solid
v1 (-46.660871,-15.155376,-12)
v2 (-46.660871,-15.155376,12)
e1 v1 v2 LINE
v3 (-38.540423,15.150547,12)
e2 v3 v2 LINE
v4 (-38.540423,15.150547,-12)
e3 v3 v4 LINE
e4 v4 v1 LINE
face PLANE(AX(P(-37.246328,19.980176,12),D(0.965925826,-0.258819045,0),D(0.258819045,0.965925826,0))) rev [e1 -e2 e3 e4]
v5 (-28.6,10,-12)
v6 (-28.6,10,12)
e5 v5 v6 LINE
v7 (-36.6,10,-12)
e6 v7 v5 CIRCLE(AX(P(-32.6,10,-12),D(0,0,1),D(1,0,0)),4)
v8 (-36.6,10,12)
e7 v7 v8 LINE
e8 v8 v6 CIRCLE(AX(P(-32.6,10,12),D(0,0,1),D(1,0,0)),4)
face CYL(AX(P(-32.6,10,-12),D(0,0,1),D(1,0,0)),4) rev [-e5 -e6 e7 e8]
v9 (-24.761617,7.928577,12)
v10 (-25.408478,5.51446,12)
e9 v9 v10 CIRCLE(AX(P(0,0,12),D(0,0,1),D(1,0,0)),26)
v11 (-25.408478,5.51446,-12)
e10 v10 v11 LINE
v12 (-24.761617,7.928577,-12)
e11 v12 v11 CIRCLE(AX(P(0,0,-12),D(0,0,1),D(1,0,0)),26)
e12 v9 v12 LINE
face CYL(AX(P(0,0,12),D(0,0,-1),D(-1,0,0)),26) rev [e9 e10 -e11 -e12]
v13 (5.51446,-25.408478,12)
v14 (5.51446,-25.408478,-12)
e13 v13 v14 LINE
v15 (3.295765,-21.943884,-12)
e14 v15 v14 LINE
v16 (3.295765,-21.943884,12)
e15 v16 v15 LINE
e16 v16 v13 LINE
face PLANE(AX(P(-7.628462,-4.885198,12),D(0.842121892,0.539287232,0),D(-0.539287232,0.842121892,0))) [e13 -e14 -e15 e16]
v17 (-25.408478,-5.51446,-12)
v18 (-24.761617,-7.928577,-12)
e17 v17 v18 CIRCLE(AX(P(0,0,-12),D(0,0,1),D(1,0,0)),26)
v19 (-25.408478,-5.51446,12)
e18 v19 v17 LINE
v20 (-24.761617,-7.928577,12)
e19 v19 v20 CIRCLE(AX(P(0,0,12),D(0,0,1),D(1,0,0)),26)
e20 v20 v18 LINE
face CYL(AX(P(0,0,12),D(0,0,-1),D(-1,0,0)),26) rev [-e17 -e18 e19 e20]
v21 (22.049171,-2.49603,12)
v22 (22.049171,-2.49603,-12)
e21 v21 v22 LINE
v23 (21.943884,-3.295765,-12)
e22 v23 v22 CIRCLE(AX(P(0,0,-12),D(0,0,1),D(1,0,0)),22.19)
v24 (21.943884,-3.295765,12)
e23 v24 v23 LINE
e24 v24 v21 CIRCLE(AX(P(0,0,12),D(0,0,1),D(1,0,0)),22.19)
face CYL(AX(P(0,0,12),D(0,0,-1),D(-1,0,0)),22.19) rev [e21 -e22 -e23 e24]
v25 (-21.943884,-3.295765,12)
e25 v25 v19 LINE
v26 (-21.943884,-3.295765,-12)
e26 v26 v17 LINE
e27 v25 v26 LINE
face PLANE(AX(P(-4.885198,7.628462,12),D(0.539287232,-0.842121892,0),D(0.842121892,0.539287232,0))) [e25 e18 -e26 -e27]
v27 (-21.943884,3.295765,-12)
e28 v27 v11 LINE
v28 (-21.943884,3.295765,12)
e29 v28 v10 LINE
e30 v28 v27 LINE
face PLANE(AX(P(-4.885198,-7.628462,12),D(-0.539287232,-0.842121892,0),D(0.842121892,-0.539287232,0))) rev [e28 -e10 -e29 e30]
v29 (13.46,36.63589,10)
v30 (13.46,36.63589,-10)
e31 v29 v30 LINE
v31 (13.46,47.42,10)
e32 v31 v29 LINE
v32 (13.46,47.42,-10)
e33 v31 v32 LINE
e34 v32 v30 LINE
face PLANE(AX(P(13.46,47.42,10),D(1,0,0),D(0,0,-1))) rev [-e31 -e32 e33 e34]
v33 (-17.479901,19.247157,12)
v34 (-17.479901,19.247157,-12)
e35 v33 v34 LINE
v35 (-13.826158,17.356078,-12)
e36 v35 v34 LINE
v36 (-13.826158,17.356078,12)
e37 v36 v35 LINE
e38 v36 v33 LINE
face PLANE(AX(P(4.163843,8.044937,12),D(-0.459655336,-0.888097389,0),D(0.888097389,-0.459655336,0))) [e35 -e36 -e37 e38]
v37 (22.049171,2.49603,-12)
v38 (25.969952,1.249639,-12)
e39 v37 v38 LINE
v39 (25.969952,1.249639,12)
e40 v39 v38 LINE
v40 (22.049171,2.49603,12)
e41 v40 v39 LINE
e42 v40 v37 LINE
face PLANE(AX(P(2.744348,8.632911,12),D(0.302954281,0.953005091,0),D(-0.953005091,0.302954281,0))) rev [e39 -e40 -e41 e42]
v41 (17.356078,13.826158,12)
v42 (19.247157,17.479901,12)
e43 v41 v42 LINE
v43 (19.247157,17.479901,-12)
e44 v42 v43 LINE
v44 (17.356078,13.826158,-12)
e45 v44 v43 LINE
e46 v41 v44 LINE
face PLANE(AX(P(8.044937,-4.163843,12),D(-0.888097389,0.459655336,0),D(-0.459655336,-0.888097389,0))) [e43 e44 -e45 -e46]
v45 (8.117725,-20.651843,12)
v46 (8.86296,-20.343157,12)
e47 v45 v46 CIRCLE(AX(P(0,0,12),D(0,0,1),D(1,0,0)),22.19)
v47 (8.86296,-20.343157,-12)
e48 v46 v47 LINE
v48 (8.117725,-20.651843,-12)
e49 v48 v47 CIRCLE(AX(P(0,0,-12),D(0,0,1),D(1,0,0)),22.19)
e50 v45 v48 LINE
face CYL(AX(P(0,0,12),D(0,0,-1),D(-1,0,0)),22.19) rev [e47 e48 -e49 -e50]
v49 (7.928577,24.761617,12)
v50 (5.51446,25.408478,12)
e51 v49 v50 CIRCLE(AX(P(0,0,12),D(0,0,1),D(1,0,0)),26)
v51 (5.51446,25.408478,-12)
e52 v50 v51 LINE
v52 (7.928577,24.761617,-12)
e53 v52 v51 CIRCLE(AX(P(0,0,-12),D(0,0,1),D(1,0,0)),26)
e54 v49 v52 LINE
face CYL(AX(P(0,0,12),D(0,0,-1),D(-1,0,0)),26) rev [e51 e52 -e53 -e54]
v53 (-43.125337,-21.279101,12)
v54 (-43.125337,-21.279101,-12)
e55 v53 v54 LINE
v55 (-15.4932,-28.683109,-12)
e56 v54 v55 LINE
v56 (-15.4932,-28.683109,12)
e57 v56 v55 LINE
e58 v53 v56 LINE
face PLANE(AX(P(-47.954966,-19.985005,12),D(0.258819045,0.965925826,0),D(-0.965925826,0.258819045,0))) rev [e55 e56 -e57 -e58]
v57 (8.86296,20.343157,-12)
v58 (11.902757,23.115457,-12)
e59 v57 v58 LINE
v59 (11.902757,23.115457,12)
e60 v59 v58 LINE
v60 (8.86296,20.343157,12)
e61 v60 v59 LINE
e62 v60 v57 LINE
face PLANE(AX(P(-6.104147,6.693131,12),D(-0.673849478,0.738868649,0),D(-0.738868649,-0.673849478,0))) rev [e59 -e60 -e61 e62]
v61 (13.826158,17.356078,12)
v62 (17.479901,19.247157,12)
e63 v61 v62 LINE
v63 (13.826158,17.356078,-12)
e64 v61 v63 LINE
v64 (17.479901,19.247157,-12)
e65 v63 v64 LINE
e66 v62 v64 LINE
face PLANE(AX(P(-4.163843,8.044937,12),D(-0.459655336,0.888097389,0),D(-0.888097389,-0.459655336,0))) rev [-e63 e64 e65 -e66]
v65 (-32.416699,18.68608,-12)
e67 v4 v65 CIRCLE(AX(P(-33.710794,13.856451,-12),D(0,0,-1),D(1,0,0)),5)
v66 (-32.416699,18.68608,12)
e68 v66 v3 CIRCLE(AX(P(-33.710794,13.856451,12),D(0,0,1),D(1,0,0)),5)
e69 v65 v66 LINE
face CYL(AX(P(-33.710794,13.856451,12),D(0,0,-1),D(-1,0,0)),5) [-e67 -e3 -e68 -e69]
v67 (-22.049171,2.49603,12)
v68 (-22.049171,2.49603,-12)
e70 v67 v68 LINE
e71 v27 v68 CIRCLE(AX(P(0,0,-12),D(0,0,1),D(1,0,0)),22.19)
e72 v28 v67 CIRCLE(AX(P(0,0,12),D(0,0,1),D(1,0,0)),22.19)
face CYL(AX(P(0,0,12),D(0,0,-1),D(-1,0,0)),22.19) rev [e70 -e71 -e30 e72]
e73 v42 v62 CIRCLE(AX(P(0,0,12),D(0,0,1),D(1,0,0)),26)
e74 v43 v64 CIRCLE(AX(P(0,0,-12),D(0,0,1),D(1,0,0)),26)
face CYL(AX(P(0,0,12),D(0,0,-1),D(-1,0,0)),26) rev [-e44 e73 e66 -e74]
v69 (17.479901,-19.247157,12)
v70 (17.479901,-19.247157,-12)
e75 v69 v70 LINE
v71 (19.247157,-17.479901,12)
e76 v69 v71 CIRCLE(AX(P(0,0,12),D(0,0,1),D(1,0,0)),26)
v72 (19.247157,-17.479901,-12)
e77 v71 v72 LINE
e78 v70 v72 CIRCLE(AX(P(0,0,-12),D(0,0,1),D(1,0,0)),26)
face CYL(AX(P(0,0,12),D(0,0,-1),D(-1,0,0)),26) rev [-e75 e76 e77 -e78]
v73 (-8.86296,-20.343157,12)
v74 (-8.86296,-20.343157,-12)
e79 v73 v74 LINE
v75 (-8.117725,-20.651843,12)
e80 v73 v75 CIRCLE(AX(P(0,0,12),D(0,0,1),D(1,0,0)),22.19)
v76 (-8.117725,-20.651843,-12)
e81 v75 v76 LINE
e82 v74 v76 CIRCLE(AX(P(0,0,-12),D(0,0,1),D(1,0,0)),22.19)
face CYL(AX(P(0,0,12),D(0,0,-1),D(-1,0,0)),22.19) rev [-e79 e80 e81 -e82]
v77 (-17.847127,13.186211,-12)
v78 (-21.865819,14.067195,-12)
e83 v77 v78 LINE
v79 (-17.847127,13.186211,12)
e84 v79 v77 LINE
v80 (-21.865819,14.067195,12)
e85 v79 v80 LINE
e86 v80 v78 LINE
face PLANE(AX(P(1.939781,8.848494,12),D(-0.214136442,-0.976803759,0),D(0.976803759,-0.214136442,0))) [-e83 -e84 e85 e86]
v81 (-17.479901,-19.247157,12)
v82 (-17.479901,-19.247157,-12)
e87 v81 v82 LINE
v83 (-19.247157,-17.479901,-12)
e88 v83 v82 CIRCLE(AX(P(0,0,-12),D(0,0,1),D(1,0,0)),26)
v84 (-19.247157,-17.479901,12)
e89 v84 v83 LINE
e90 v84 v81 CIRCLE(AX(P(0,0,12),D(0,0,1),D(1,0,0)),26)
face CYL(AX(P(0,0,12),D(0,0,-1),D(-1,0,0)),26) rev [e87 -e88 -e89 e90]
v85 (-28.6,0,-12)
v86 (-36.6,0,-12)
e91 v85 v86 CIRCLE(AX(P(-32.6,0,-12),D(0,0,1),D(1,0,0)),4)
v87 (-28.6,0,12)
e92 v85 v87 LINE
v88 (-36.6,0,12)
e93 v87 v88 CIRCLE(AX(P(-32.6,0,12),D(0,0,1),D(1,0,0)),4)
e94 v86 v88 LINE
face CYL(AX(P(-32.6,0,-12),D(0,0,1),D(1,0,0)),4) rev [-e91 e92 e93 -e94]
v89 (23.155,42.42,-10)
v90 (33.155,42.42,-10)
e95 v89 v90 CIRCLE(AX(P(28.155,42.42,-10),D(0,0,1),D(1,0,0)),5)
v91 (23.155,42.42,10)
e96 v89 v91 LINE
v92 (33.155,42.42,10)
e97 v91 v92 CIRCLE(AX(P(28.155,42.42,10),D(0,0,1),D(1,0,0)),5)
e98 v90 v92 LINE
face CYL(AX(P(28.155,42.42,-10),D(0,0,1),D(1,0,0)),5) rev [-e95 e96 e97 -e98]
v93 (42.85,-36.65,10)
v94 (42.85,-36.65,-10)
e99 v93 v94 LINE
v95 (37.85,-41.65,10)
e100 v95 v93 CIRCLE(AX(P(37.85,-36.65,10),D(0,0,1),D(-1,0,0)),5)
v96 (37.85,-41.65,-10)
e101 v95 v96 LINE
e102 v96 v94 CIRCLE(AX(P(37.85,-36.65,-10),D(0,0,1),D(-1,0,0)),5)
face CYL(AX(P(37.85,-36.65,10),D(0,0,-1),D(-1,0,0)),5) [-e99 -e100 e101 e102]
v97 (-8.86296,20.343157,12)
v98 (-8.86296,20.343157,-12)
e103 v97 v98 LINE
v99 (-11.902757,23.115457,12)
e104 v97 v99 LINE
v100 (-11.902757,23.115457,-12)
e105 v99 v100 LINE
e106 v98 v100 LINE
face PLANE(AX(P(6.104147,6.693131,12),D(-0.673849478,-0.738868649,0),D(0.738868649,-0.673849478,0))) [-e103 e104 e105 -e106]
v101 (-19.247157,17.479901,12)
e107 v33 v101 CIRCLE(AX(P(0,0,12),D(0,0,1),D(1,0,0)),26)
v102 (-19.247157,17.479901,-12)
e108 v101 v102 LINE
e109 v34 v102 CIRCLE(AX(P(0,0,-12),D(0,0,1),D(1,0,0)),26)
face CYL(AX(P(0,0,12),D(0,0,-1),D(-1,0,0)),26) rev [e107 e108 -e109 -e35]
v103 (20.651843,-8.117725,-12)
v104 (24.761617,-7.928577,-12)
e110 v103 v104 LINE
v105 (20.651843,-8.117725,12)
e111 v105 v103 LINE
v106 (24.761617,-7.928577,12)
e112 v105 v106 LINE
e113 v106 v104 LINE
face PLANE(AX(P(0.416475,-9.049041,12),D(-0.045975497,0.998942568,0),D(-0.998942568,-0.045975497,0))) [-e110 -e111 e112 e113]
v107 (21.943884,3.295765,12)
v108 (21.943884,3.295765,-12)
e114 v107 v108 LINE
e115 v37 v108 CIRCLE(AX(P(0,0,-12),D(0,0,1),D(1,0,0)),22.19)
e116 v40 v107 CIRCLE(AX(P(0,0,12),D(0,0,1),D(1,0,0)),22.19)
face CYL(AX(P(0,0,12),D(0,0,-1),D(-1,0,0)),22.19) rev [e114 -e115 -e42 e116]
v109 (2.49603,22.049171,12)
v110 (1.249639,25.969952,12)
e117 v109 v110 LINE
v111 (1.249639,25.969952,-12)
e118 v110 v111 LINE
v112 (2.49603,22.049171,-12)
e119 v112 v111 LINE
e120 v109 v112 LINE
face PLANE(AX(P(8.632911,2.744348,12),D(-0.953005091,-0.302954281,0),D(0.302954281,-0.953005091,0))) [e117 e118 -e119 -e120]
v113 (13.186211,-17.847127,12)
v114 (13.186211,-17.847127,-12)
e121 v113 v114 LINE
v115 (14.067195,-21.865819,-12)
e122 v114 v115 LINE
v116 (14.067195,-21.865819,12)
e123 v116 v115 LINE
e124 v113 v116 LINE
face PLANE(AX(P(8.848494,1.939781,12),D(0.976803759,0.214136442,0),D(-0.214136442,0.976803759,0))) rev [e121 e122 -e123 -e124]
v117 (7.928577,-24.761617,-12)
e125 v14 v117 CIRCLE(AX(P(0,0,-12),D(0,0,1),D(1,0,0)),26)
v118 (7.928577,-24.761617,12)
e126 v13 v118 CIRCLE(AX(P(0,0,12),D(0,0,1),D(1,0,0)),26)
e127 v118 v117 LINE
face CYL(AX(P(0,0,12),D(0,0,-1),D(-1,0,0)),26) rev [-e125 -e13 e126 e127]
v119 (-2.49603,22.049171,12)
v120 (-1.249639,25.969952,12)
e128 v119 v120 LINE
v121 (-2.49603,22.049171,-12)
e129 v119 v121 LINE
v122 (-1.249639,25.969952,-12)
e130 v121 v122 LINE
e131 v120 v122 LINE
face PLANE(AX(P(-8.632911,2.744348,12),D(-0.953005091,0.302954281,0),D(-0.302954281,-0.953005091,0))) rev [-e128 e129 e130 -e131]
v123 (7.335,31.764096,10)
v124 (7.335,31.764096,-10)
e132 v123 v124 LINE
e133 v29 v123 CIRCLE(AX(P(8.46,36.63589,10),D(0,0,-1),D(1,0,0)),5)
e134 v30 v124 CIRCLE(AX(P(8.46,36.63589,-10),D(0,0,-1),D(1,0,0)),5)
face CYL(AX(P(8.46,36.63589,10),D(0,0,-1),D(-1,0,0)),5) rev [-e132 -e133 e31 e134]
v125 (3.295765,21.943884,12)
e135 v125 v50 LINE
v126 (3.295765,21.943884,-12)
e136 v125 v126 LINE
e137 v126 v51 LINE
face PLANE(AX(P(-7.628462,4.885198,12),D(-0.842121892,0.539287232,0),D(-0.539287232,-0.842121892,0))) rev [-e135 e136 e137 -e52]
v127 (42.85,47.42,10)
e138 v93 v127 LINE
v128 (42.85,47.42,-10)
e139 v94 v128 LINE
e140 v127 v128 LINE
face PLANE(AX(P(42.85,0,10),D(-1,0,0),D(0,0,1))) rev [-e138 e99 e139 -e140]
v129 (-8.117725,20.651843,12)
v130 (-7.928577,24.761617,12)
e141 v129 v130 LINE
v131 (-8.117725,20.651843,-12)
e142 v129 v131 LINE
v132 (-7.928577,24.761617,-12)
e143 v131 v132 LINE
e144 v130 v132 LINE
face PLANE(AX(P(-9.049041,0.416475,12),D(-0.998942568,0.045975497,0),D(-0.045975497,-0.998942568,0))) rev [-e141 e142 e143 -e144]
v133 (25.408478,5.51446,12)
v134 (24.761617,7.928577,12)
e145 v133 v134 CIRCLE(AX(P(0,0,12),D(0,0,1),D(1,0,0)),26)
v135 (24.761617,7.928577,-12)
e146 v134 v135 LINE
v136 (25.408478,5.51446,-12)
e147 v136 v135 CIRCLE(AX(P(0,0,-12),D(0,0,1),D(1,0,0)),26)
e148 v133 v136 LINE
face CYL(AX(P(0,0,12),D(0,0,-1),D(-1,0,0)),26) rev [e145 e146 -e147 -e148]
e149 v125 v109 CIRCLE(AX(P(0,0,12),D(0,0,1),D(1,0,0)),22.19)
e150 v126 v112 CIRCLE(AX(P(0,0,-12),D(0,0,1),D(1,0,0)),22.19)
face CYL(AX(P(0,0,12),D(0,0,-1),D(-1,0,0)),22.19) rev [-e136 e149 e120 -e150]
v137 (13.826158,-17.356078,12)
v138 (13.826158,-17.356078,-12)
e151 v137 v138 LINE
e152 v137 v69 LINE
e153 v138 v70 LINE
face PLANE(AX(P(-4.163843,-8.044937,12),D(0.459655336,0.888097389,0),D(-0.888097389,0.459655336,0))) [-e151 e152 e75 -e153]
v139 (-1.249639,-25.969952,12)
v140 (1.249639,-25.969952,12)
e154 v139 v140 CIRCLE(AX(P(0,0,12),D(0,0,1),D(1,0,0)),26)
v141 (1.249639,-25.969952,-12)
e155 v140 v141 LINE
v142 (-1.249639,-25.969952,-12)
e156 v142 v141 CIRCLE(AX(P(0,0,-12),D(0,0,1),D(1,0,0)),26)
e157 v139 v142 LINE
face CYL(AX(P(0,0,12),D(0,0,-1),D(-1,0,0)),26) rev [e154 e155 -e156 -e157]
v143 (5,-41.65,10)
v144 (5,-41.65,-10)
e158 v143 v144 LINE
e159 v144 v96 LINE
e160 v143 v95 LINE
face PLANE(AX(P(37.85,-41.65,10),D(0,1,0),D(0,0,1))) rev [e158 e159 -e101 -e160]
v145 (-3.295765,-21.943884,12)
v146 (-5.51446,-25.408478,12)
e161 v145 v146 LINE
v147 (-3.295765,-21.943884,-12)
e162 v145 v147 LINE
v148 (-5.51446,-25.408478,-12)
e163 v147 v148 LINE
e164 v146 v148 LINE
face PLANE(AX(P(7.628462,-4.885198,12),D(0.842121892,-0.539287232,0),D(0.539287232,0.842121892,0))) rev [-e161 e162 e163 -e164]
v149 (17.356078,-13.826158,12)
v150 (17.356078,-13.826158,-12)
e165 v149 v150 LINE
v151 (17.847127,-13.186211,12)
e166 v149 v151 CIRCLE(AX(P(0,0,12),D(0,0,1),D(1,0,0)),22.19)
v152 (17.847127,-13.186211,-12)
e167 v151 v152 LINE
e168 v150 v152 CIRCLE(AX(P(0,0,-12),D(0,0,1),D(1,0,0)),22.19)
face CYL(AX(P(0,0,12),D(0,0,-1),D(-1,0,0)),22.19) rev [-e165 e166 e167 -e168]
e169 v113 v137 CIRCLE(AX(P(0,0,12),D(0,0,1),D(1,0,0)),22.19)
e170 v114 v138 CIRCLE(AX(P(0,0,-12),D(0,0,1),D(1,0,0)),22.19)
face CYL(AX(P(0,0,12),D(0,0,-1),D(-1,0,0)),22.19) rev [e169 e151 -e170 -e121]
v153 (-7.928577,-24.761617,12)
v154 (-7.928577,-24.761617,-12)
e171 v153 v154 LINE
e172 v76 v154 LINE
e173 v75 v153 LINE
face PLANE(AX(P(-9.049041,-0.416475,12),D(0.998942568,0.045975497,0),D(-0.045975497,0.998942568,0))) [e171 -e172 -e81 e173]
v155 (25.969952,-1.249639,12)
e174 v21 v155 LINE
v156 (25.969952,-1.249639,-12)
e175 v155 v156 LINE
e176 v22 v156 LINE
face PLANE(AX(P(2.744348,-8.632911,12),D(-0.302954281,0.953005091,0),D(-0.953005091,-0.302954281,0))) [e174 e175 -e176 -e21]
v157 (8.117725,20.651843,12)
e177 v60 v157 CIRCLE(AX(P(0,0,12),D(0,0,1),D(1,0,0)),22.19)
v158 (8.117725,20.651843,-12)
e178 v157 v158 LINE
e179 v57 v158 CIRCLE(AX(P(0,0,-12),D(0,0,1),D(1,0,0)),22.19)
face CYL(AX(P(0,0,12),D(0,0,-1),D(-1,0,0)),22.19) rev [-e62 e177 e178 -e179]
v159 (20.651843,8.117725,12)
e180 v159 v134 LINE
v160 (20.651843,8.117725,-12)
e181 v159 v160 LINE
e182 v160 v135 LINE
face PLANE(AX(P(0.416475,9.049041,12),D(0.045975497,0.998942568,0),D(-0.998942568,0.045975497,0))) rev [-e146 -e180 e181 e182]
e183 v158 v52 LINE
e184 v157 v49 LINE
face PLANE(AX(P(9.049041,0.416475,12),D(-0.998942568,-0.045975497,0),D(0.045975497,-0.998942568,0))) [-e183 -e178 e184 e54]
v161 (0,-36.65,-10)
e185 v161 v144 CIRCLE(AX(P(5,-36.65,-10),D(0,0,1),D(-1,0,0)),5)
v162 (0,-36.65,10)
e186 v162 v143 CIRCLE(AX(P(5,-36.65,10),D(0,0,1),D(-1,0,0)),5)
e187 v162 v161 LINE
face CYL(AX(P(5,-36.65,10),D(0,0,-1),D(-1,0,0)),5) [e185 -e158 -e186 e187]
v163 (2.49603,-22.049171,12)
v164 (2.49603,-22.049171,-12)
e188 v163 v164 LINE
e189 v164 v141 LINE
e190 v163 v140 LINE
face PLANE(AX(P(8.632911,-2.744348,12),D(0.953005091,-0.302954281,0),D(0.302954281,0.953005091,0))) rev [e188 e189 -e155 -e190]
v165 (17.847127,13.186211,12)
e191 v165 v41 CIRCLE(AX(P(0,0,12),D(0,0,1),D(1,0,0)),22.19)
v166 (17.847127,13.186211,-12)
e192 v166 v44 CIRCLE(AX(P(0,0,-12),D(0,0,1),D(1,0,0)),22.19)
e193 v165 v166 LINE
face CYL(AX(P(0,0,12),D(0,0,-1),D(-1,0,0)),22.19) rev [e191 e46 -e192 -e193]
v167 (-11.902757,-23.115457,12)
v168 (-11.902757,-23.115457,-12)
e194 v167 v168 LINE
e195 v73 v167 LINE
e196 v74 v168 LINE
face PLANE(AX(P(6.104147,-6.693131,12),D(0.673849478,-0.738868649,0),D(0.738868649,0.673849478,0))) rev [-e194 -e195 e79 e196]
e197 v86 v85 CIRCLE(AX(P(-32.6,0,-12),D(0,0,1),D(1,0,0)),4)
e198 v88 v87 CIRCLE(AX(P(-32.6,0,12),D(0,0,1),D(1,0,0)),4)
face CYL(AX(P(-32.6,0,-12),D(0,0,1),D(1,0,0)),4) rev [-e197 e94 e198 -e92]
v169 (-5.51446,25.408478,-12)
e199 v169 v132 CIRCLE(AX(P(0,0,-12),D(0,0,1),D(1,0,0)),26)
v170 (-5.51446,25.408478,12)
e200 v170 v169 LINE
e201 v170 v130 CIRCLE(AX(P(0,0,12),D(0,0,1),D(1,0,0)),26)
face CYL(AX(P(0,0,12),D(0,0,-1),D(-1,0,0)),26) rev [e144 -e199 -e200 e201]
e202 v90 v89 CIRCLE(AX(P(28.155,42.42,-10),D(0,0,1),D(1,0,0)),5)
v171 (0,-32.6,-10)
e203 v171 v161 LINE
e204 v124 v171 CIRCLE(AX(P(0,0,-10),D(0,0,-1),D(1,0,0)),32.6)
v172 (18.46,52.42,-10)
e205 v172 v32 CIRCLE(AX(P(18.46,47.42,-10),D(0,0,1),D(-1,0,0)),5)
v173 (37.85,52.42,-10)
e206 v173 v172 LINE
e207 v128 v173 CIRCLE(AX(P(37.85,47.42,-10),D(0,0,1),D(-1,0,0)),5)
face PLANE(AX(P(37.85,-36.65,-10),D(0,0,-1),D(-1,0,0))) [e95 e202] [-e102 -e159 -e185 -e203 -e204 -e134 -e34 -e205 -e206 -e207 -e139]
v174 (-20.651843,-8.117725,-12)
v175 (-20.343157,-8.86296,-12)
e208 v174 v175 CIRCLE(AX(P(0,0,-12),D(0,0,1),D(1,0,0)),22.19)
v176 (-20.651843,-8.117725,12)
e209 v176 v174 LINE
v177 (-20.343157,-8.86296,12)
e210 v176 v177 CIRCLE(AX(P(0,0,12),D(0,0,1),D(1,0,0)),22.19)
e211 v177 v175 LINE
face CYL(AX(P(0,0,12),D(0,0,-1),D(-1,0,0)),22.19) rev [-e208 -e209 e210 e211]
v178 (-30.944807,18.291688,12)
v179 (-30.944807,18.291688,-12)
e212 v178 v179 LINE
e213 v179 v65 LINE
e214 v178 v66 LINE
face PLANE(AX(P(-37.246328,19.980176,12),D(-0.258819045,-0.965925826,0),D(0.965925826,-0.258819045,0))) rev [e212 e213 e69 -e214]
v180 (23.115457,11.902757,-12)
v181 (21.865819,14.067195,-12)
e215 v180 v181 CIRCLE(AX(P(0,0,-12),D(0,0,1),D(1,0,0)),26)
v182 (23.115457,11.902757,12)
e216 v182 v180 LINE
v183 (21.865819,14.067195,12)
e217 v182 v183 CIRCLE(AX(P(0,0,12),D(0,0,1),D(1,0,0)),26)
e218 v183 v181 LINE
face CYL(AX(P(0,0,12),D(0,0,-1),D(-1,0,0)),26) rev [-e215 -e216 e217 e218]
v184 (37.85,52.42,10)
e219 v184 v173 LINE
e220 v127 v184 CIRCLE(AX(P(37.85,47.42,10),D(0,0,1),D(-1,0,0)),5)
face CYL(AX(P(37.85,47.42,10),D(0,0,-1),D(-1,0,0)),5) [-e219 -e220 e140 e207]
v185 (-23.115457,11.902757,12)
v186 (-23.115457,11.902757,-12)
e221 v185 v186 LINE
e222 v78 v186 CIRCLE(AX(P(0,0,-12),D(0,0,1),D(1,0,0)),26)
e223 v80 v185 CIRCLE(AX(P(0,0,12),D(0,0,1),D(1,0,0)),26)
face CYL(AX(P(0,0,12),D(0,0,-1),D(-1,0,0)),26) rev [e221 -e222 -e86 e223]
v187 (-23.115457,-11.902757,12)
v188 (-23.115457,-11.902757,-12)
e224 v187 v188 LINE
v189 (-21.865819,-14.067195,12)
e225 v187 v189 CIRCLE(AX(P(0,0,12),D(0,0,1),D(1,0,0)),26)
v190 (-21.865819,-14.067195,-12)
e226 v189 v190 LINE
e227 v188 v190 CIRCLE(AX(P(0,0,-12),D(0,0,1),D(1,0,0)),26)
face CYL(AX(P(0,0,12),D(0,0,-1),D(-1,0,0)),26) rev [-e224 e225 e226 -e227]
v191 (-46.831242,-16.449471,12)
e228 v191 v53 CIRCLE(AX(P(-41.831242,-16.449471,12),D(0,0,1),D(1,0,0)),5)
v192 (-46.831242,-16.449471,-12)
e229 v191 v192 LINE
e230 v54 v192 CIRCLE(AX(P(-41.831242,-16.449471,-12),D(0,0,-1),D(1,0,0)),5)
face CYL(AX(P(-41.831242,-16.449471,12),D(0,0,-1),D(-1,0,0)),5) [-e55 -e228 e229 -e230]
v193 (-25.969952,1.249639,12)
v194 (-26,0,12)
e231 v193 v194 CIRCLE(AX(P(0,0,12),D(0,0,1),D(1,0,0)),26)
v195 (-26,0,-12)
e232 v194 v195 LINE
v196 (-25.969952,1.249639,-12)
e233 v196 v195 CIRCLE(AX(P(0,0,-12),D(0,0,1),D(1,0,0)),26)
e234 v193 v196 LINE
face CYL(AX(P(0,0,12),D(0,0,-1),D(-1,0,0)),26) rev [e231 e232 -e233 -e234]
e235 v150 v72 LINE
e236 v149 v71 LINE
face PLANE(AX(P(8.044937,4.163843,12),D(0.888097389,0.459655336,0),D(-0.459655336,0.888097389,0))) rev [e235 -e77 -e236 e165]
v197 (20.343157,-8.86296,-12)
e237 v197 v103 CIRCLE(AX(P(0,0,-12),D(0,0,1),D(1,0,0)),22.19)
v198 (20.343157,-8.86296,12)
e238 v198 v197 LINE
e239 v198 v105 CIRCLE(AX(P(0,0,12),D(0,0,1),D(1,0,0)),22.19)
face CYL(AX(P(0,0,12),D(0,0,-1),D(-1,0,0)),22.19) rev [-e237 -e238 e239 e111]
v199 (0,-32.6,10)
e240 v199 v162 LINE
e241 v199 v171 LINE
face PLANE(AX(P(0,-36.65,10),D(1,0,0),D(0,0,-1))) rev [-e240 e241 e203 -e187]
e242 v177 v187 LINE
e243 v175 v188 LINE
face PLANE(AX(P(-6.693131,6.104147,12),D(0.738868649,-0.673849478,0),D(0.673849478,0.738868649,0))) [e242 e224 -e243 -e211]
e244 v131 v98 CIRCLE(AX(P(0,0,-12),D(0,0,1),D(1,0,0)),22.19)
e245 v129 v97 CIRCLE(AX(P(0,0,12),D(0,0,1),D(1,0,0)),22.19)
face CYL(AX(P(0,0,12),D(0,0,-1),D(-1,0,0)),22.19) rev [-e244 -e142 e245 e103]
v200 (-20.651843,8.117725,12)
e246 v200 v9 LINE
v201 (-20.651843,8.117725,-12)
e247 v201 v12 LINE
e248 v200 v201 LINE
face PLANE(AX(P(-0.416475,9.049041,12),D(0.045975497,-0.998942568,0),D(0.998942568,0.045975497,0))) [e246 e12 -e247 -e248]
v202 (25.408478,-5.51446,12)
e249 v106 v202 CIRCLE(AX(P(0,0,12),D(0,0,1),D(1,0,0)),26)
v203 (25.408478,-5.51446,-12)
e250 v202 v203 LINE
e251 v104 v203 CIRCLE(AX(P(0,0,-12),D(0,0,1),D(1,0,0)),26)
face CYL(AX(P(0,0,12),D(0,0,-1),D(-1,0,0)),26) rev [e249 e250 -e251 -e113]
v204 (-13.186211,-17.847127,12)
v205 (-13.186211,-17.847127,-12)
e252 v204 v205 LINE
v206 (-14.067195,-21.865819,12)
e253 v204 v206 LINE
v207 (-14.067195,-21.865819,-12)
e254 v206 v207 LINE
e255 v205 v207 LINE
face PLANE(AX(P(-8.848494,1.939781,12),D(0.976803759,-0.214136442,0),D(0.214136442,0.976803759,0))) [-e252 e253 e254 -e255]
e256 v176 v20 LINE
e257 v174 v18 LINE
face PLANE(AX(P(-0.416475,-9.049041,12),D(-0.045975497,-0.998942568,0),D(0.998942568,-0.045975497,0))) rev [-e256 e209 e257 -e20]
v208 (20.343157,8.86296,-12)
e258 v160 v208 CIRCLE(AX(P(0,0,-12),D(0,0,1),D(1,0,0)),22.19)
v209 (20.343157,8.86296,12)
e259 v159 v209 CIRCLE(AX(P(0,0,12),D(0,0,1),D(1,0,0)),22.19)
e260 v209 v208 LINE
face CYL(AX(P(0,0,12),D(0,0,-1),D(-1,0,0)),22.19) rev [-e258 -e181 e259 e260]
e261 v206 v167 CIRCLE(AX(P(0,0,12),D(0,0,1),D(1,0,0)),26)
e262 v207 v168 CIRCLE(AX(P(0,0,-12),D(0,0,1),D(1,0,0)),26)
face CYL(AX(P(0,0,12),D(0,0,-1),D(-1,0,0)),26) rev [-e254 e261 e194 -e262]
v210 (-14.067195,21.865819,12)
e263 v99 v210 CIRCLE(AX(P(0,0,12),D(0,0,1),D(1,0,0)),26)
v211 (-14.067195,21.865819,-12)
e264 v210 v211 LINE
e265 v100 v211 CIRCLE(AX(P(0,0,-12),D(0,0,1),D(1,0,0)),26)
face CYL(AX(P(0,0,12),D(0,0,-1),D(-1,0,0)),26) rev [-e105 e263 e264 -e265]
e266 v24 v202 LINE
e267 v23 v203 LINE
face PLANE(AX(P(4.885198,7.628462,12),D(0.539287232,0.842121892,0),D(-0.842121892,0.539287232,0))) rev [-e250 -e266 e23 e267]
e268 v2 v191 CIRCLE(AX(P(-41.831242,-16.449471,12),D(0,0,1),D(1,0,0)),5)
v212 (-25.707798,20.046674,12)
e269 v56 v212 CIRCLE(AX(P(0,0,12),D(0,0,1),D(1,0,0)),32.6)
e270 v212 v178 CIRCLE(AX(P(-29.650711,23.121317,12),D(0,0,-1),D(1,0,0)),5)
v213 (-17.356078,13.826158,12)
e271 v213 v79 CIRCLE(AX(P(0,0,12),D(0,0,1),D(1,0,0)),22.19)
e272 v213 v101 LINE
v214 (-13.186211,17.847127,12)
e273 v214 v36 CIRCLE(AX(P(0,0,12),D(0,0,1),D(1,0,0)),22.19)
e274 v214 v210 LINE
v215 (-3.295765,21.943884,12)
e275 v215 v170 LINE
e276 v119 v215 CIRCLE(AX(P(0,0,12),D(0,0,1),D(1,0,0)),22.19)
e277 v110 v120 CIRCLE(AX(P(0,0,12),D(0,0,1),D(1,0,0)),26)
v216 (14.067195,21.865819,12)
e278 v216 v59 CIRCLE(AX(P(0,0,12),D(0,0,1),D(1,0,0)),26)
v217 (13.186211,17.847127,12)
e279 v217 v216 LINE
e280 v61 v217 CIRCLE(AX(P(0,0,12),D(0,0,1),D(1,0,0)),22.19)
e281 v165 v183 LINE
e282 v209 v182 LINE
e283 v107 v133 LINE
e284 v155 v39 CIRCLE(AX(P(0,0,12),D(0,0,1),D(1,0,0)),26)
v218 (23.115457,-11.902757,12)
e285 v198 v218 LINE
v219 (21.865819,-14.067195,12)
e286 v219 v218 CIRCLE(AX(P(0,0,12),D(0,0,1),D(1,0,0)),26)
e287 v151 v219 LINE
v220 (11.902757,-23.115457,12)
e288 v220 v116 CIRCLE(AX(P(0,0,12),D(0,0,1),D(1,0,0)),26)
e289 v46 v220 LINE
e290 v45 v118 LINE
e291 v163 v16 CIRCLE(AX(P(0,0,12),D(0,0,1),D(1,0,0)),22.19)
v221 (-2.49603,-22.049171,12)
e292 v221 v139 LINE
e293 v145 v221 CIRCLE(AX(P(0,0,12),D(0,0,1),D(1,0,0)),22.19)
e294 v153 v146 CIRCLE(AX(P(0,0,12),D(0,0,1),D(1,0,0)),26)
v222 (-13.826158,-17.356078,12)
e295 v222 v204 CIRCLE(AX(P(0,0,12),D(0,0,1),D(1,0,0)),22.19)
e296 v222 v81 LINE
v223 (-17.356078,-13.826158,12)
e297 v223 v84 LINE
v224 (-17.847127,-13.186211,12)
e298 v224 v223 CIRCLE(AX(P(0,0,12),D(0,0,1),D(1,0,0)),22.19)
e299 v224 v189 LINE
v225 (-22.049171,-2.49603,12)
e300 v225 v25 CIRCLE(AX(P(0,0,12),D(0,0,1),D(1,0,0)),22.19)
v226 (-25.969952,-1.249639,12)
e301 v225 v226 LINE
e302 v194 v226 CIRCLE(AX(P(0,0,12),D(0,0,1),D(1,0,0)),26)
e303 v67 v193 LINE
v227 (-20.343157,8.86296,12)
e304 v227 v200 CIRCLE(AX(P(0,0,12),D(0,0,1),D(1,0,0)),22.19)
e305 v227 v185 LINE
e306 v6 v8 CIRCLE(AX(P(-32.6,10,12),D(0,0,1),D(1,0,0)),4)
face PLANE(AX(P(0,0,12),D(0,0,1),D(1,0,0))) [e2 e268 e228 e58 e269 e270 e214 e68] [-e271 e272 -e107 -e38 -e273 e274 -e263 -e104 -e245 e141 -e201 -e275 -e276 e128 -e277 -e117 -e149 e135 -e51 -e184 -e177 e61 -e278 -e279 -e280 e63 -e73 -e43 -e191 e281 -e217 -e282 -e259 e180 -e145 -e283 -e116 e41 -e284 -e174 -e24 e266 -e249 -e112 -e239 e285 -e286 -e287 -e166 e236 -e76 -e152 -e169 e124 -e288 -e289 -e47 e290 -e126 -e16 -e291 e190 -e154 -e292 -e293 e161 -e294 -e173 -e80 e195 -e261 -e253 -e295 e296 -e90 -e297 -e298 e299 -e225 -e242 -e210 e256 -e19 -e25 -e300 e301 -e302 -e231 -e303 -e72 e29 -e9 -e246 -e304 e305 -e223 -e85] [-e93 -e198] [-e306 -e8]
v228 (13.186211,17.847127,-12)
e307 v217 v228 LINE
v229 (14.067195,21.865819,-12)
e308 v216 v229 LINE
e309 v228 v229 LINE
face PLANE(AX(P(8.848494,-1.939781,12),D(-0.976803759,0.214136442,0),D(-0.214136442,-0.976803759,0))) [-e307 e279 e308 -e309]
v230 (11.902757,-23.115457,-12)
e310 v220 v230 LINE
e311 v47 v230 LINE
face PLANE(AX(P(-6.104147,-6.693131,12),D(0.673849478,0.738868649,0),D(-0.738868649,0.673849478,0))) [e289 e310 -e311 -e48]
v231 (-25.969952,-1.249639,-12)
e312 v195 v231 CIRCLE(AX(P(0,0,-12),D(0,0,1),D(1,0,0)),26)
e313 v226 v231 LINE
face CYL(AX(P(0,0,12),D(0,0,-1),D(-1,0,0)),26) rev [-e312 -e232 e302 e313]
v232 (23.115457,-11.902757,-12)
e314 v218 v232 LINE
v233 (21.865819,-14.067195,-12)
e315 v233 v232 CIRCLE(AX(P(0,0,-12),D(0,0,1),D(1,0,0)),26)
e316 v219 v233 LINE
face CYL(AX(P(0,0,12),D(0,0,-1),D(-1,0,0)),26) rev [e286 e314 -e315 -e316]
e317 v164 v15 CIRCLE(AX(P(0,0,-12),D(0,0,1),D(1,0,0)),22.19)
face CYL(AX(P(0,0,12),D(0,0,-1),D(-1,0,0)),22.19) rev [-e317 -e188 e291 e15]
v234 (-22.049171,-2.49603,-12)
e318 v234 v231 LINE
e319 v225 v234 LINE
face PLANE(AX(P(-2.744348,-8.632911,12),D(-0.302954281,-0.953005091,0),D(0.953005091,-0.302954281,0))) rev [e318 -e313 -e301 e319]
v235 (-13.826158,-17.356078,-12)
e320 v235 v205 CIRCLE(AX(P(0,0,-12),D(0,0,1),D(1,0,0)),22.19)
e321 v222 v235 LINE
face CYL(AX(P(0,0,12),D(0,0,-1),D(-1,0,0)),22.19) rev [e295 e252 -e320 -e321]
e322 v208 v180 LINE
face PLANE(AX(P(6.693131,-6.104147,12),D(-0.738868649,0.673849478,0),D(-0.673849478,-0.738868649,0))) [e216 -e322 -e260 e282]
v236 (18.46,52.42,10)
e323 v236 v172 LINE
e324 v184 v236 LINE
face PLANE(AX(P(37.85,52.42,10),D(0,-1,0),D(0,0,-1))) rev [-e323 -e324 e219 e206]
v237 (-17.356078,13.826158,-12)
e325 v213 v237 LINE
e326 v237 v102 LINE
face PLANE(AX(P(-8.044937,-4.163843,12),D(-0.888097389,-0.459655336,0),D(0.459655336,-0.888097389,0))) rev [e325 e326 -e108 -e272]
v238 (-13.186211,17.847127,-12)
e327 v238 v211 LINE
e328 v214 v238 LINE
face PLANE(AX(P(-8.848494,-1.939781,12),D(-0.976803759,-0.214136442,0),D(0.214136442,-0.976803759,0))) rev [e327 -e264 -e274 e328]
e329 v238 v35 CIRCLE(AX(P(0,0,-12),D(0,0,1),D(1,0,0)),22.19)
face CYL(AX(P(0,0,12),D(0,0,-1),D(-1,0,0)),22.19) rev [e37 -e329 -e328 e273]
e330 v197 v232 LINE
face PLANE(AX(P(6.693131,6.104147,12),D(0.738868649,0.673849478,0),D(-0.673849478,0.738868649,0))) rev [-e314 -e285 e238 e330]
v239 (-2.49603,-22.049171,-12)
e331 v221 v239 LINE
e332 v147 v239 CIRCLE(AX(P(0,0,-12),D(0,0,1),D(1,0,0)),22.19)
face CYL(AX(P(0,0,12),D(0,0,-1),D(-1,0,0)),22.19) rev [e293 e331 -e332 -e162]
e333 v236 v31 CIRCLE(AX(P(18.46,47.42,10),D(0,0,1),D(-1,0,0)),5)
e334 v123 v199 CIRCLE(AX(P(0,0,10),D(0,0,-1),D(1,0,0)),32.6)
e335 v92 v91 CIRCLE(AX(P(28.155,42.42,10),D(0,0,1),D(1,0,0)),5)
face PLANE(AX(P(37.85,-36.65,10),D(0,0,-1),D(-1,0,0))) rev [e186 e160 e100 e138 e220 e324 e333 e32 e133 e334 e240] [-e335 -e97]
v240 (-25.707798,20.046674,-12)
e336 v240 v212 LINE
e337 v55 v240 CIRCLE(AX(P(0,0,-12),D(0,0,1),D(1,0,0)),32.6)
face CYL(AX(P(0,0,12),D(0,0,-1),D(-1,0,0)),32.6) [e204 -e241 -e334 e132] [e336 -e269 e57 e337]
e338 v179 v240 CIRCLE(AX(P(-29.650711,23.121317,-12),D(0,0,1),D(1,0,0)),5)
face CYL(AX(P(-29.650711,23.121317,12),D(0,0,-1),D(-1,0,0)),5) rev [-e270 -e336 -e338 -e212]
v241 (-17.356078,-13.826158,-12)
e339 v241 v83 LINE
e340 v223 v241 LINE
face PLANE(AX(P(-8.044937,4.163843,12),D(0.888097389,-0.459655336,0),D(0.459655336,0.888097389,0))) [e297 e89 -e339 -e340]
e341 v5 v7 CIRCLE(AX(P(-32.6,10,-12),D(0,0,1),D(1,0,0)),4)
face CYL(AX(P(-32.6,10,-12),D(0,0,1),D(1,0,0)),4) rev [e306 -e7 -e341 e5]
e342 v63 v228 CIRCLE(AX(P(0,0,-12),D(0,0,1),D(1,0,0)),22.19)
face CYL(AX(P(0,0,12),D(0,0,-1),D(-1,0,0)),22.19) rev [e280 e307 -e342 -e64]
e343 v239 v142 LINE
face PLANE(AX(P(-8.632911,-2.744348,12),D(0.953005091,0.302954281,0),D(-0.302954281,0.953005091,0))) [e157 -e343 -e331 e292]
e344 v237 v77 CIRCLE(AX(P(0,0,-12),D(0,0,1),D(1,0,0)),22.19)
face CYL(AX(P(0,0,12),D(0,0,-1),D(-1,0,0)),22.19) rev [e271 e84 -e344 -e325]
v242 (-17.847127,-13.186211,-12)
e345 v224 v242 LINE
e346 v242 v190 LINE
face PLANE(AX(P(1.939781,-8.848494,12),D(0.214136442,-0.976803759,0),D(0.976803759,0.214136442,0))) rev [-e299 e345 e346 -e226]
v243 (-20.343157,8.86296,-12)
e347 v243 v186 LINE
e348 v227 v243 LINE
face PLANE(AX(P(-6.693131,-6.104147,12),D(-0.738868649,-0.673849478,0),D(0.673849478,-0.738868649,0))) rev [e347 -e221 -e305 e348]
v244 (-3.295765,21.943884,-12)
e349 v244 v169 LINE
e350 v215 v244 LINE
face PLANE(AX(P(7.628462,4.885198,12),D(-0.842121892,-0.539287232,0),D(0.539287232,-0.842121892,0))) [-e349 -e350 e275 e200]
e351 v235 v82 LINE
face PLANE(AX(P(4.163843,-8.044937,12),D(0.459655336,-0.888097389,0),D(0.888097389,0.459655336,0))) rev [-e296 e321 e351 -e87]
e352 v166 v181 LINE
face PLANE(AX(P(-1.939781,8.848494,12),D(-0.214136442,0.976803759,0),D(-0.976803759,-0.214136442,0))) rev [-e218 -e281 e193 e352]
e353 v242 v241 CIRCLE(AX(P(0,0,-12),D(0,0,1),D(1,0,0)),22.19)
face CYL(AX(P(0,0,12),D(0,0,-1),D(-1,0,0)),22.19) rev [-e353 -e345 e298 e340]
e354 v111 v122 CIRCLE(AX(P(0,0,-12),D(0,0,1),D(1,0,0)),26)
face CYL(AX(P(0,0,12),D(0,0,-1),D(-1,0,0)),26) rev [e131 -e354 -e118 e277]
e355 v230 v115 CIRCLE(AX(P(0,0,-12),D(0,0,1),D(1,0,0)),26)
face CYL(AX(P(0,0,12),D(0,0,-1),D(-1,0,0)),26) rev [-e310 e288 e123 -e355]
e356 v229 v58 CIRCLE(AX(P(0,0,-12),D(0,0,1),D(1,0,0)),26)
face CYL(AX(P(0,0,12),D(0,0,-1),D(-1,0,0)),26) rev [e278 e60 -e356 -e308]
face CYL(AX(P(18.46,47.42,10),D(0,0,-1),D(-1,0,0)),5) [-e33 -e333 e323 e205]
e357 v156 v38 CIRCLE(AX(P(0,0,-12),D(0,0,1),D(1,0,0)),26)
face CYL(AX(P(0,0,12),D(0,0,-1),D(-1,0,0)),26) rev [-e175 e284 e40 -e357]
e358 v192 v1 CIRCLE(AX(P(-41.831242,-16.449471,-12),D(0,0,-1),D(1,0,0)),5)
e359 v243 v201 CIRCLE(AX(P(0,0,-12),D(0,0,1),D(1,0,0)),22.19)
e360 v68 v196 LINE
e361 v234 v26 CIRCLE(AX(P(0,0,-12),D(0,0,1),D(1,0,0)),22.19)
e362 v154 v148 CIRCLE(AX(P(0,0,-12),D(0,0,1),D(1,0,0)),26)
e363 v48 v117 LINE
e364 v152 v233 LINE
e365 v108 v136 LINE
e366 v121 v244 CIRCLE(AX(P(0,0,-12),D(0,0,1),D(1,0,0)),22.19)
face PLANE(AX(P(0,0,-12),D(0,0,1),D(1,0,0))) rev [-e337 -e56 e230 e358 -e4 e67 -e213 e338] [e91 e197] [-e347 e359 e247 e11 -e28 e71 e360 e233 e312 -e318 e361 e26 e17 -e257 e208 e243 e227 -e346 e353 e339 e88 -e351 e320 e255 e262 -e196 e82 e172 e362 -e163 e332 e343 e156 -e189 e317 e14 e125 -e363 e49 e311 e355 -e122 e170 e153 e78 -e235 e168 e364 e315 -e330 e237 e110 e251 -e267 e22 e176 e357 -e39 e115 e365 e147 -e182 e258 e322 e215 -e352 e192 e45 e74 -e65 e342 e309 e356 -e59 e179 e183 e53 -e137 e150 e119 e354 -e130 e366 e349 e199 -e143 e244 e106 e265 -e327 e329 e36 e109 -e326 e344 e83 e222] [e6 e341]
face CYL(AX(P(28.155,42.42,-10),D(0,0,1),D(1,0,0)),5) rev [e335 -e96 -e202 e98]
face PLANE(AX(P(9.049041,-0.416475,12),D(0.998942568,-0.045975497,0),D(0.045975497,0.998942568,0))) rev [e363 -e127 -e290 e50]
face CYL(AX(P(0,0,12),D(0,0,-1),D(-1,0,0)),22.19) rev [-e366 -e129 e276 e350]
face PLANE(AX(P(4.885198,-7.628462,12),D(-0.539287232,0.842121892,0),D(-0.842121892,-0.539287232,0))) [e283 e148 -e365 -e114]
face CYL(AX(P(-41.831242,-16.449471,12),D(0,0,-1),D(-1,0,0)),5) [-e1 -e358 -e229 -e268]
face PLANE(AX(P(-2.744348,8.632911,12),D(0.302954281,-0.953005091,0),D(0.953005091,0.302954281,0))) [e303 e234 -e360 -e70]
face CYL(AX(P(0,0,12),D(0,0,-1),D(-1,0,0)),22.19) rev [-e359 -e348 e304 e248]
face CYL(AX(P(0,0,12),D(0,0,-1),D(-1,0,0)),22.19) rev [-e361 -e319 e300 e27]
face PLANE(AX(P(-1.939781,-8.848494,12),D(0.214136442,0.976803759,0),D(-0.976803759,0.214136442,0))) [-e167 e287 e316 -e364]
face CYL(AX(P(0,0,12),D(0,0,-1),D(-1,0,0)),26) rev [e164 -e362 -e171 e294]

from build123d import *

# Parameters (mm, degrees)
SPLINED_HUB_PROFILE_R   = 32.6
SPLINED_HUB_24T_DEPTH   = 12
MOUNTING_FLANGE_DEPTH   = 10
SIDE_LUG_DEPTH          = 12
LUG_HOLE_PROFILE_R      = 5
LUG_HOLE_10_DEPTH       = 10
LUG_FILLET_R5_R         = 5
FLANGE_HOLES_PROFILE_R  = 4
FLANGE_HOLES_2X_8_DEPTH = 74.654745929
FLANGE_SLOT_PROFILE_R   = 4
FLANGE_SLOT_DEPTH       = 12


with BuildPart() as part:
    # Splined Hub Profile → Splined Hub 24T (new, symmetric)
    with BuildSketch(Plane.XY):
        Circle(SPLINED_HUB_PROFILE_R)
        with BuildLine():
            ThreePointArc((25.969951923, 1.249638793), (25.992486895, 0.625), (26, 0))
            ThreePointArc((26, 0), (25.992486895, -0.625), (25.969951923, -1.249638793))
            Line((25.969951923, -1.249638793), (22.049170798, -2.496030275))
            ThreePointArc((22.049170798, -2.496030275), (22.000161474, -2.896376205), (21.943883694, -3.295765225))
            Line((21.943883694, -3.295765225), (25.408477589, -5.514459774))
            ThreePointArc((25.408477589, -5.514459774), (25.114071484, -6.729295173), (24.761616951, -7.928576542))
            Line((24.761616951, -7.928576542), (20.651843349, -8.117725437))
            ThreePointArc((20.651843349, -8.117725437), (20.500886826, -8.491745364), (20.343157181, -8.862959772))
            Line((20.343157181, -8.862959772), (23.115457497, -11.902757021))
            ThreePointArc((23.115457497, -11.902757021), (22.516660498, -13), (21.865818704, -14.067194902))
            Line((21.865818704, -14.067194902), (17.847126905, -13.186211026))
            ThreePointArc((17.847126905, -13.186211026), (17.604510621, -13.50841611), (17.356078124, -13.826158257))
            Line((17.356078124, -13.826158257), (19.247157176, -17.479901047))
            ThreePointArc((19.247157176, -17.479901047), (18.384776311, -18.384776311), (17.479901047, -19.247157176))
            Line((17.479901047, -19.247157176), (13.826158257, -17.356078124))
            ThreePointArc((13.826158257, -17.356078124), (13.50841611, -17.604510621), (13.186211026, -17.847126905))
            Line((13.186211026, -17.847126905), (14.067194902, -21.865818704))
            ThreePointArc((14.067194902, -21.865818704), (13, -22.516660498), (11.902757021, -23.115457497))
            Line((11.902757021, -23.115457497), (8.862959772, -20.343157181))
            ThreePointArc((8.862959772, -20.343157181), (8.491745364, -20.500886826), (8.117725437, -20.651843349))
            Line((8.117725437, -20.651843349), (7.928576542, -24.761616951))
            ThreePointArc((7.928576542, -24.761616951), (6.729295173, -25.114071484), (5.514459774, -25.408477589))
            Line((5.514459774, -25.408477589), (3.295765225, -21.943883694))
            ThreePointArc((3.295765225, -21.943883694), (2.896376205, -22.000161474), (2.496030275, -22.049170798))
            Line((2.496030275, -22.049170798), (1.249638793, -25.969951923))
            ThreePointArc((1.249638793, -25.969951923), (0, -26), (-1.249638793, -25.969951923))
            Line((-1.249638793, -25.969951923), (-2.496030275, -22.049170798))
            ThreePointArc((-2.496030275, -22.049170798), (-2.896376205, -22.000161474), (-3.295765225, -21.943883694))
            Line((-3.295765225, -21.943883694), (-5.514459774, -25.408477589))
            ThreePointArc((-5.514459774, -25.408477589), (-6.729295173, -25.114071484), (-7.928576542, -24.761616951))
            Line((-7.928576542, -24.761616951), (-8.117725437, -20.651843349))
            ThreePointArc((-8.117725437, -20.651843349), (-8.491745364, -20.500886826), (-8.862959772, -20.343157181))
            Line((-8.862959772, -20.343157181), (-11.902757021, -23.115457497))
            ThreePointArc((-11.902757021, -23.115457497), (-13, -22.516660498), (-14.067194902, -21.865818704))
            Line((-14.067194902, -21.865818704), (-13.186211026, -17.847126905))
            ThreePointArc((-13.186211026, -17.847126905), (-13.50841611, -17.604510621), (-13.826158257, -17.356078124))
            Line((-13.826158257, -17.356078124), (-17.479901047, -19.247157176))
            ThreePointArc((-17.479901047, -19.247157176), (-18.384776311, -18.384776311), (-19.247157176, -17.479901047))
            Line((-19.247157176, -17.479901047), (-17.356078124, -13.826158257))
            ThreePointArc((-17.356078124, -13.826158257), (-17.604510621, -13.50841611), (-17.847126905, -13.186211026))
            Line((-17.847126905, -13.186211026), (-21.865818704, -14.067194902))
            ThreePointArc((-21.865818704, -14.067194902), (-22.516660498, -13), (-23.115457497, -11.902757021))
            Line((-23.115457497, -11.902757021), (-20.343157181, -8.862959772))
            ThreePointArc((-20.343157181, -8.862959772), (-20.500886826, -8.491745364), (-20.651843349, -8.117725437))
            Line((-20.651843349, -8.117725437), (-24.761616951, -7.928576542))
            ThreePointArc((-24.761616951, -7.928576542), (-25.114071484, -6.729295173), (-25.408477589, -5.514459774))
            Line((-25.408477589, -5.514459774), (-21.943883694, -3.295765225))
            ThreePointArc((-21.943883694, -3.295765225), (-22.000161474, -2.896376205), (-22.049170798, -2.496030275))
            Line((-22.049170798, -2.496030275), (-25.969951923, -1.249638793))
            ThreePointArc((-25.969951923, -1.249638793), (-26, 0), (-25.969951923, 1.249638793))
            Line((-25.969951923, 1.249638793), (-22.049170798, 2.496030275))
            ThreePointArc((-22.049170798, 2.496030275), (-22.000161474, 2.896376205), (-21.943883694, 3.295765225))
            Line((-21.943883694, 3.295765225), (-25.408477589, 5.514459774))
            ThreePointArc((-25.408477589, 5.514459774), (-25.114071484, 6.729295173), (-24.761616951, 7.928576542))
            Line((-24.761616951, 7.928576542), (-20.651843349, 8.117725437))
            ThreePointArc((-20.651843349, 8.117725437), (-20.500886826, 8.491745364), (-20.343157181, 8.862959772))
            Line((-20.343157181, 8.862959772), (-23.115457497, 11.902757021))
            ThreePointArc((-23.115457497, 11.902757021), (-22.516660498, 13), (-21.865818704, 14.067194902))
            Line((-21.865818704, 14.067194902), (-17.847126905, 13.186211026))
            ThreePointArc((-17.847126905, 13.186211026), (-17.604510621, 13.50841611), (-17.356078124, 13.826158257))
            Line((-17.356078124, 13.826158257), (-19.247157176, 17.479901047))
            ThreePointArc((-19.247157176, 17.479901047), (-18.384776311, 18.384776311), (-17.479901047, 19.247157176))
            Line((-17.479901047, 19.247157176), (-13.826158257, 17.356078124))
            ThreePointArc((-13.826158257, 17.356078124), (-13.50841611, 17.604510621), (-13.186211026, 17.847126905))
            Line((-13.186211026, 17.847126905), (-14.067194902, 21.865818704))
            ThreePointArc((-14.067194902, 21.865818704), (-13, 22.516660498), (-11.902757021, 23.115457497))
            Line((-11.902757021, 23.115457497), (-8.862959772, 20.343157181))
            ThreePointArc((-8.862959772, 20.343157181), (-8.491745364, 20.500886826), (-8.117725437, 20.651843349))
            Line((-8.117725437, 20.651843349), (-7.928576542, 24.761616951))
            ThreePointArc((-7.928576542, 24.761616951), (-6.729295173, 25.114071484), (-5.514459774, 25.408477589))
            Line((-5.514459774, 25.408477589), (-3.295765225, 21.943883694))
            ThreePointArc((-3.295765225, 21.943883694), (-2.896376205, 22.000161474), (-2.496030275, 22.049170798))
            Line((-2.496030275, 22.049170798), (-1.249638793, 25.969951923))
            ThreePointArc((-1.249638793, 25.969951923), (0, 26), (1.249638793, 25.969951923))
            Line((1.249638793, 25.969951923), (2.496030275, 22.049170798))
            ThreePointArc((2.496030275, 22.049170798), (2.896376205, 22.000161474), (3.295765225, 21.943883694))
            Line((3.295765225, 21.943883694), (5.514459774, 25.408477589))
            ThreePointArc((5.514459774, 25.408477589), (6.729295173, 25.114071484), (7.928576542, 24.761616951))
            Line((7.928576542, 24.761616951), (8.117725437, 20.651843349))
            ThreePointArc((8.117725437, 20.651843349), (8.491745364, 20.500886826), (8.862959772, 20.343157181))
            Line((8.862959772, 20.343157181), (11.902757021, 23.115457497))
            ThreePointArc((11.902757021, 23.115457497), (13, 22.516660498), (14.067194902, 21.865818704))
            Line((14.067194902, 21.865818704), (13.186211026, 17.847126905))
            ThreePointArc((13.186211026, 17.847126905), (13.50841611, 17.604510621), (13.826158257, 17.356078124))
            Line((13.826158257, 17.356078124), (17.479901047, 19.247157176))
            ThreePointArc((17.479901047, 19.247157176), (18.384776311, 18.384776311), (19.247157176, 17.479901047))
            Line((19.247157176, 17.479901047), (17.356078124, 13.826158257))
            ThreePointArc((17.356078124, 13.826158257), (17.604510621, 13.50841611), (17.847126905, 13.186211026))
            Line((17.847126905, 13.186211026), (21.865818704, 14.067194902))
            ThreePointArc((21.865818704, 14.067194902), (22.516660498, 13), (23.115457497, 11.902757021))
            Line((23.115457497, 11.902757021), (20.343157181, 8.862959772))
            ThreePointArc((20.343157181, 8.862959772), (20.500886826, 8.491745364), (20.651843349, 8.117725437))
            Line((20.651843349, 8.117725437), (24.761616951, 7.928576542))
            ThreePointArc((24.761616951, 7.928576542), (25.114071484, 6.729295173), (25.408477589, 5.514459774))
            Line((25.408477589, 5.514459774), (21.943883694, 3.295765225))
            ThreePointArc((21.943883694, 3.295765225), (22.000161474, 2.896376205), (22.049170798, 2.496030275))
            Line((22.049170798, 2.496030275), (25.969951923, 1.249638793))
        make_face(mode=Mode.SUBTRACT)
    extrude(amount=SPLINED_HUB_24T_DEPTH, both=True)

    # Mounting Flange Profile → Mounting Flange (add, symmetric)
    with BuildSketch(Plane.XY):
        with BuildLine():
            Line((42.85, 0), (42.85, -36.65))
            ThreePointArc((42.85, -36.65), (41.385533906, -40.185533906), (37.85, -41.65))
            Line((37.85, -41.65), (5, -41.65))
            ThreePointArc((5, -41.65), (1.464466094, -40.185533906), (0, -36.65))
            Line((0, -36.65), (0, -32.6))
            ThreePointArc((0, -32.6), (32.390349794, -3.691238309), (7.335, 31.76409569))
            ThreePointArc((7.335, 31.76409569), (11.572474899, 32.722770547), (13.46, 36.635889507))
            Line((13.46, 36.635889507), (13.46, 47.42))
            ThreePointArc((13.46, 47.42), (14.924466094, 50.955533906), (18.46, 52.42))
            Line((18.46, 52.42), (37.85, 52.42))
            ThreePointArc((37.85, 52.42), (41.385533906, 50.955533906), (42.85, 47.42))
            Line((42.85, 47.42), (42.85, 0))
        make_face()
    extrude(amount=MOUNTING_FLANGE_DEPTH, both=True)

    # Side Lug Profile → Side Lug (add, symmetric)
    with BuildSketch(Plane.XY):
        with BuildLine():
            Line((-37.246328052, 19.980175717), (-47.954966043, -19.985005346))
            Line((-47.954966043, -19.985005346), (-15.493199502, -28.683109475))
            ThreePointArc((-15.493199502, -28.683109475), (-31.533730192, -8.269453439), (-27.575166089, 17.388795679))
            Line((-27.575166089, 17.388795679), (-37.246328052, 19.980175717))
        make_face()
    extrude(amount=SIDE_LUG_DEPTH, both=True)

    # Lug Hole Profile → Lug Hole Ø10 (cut, symmetric)
    with BuildSketch(Plane.XY):
        with Locations((28.155, 42.42)):
            Circle(LUG_HOLE_PROFILE_R)
    extrude(amount=LUG_HOLE_10_DEPTH, both=True, mode=Mode.SUBTRACT)

    # Lug Fillet R5
    lug_fillet_r5_edges = [part.edges().sort_by_distance(p)[0] for p in [
        (-27.575166089, 17.388795679, 0),
        (-37.246328052, 19.980175717, 0),
        (-47.954966043, -19.985005346, 0),
    ]]
    fillet(lug_fillet_r5_edges, radius=LUG_FILLET_R5_R)

    # Flange Holes Profile → Flange Holes 2xØ8 (cut, through all)
    with BuildSketch(Plane.XY.offset(10)):
        with Locations((-32.6, 0)):
            Circle(FLANGE_HOLES_PROFILE_R)
    extrude(amount=-FLANGE_HOLES_2X_8_DEPTH, mode=Mode.SUBTRACT)

    # Flange Slot Profile → Flange Slot (cut, symmetric)
    with BuildSketch(Plane.XY):
        with Locations((-32.6, 0)):
            Circle(FLANGE_SLOT_PROFILE_R)
        with Locations((-32.6, 10)):
            Circle(FLANGE_SLOT_PROFILE_R)
    extrude(amount=FLANGE_SLOT_DEPTH, both=True, mode=Mode.SUBTRACT)


solid = part.part
